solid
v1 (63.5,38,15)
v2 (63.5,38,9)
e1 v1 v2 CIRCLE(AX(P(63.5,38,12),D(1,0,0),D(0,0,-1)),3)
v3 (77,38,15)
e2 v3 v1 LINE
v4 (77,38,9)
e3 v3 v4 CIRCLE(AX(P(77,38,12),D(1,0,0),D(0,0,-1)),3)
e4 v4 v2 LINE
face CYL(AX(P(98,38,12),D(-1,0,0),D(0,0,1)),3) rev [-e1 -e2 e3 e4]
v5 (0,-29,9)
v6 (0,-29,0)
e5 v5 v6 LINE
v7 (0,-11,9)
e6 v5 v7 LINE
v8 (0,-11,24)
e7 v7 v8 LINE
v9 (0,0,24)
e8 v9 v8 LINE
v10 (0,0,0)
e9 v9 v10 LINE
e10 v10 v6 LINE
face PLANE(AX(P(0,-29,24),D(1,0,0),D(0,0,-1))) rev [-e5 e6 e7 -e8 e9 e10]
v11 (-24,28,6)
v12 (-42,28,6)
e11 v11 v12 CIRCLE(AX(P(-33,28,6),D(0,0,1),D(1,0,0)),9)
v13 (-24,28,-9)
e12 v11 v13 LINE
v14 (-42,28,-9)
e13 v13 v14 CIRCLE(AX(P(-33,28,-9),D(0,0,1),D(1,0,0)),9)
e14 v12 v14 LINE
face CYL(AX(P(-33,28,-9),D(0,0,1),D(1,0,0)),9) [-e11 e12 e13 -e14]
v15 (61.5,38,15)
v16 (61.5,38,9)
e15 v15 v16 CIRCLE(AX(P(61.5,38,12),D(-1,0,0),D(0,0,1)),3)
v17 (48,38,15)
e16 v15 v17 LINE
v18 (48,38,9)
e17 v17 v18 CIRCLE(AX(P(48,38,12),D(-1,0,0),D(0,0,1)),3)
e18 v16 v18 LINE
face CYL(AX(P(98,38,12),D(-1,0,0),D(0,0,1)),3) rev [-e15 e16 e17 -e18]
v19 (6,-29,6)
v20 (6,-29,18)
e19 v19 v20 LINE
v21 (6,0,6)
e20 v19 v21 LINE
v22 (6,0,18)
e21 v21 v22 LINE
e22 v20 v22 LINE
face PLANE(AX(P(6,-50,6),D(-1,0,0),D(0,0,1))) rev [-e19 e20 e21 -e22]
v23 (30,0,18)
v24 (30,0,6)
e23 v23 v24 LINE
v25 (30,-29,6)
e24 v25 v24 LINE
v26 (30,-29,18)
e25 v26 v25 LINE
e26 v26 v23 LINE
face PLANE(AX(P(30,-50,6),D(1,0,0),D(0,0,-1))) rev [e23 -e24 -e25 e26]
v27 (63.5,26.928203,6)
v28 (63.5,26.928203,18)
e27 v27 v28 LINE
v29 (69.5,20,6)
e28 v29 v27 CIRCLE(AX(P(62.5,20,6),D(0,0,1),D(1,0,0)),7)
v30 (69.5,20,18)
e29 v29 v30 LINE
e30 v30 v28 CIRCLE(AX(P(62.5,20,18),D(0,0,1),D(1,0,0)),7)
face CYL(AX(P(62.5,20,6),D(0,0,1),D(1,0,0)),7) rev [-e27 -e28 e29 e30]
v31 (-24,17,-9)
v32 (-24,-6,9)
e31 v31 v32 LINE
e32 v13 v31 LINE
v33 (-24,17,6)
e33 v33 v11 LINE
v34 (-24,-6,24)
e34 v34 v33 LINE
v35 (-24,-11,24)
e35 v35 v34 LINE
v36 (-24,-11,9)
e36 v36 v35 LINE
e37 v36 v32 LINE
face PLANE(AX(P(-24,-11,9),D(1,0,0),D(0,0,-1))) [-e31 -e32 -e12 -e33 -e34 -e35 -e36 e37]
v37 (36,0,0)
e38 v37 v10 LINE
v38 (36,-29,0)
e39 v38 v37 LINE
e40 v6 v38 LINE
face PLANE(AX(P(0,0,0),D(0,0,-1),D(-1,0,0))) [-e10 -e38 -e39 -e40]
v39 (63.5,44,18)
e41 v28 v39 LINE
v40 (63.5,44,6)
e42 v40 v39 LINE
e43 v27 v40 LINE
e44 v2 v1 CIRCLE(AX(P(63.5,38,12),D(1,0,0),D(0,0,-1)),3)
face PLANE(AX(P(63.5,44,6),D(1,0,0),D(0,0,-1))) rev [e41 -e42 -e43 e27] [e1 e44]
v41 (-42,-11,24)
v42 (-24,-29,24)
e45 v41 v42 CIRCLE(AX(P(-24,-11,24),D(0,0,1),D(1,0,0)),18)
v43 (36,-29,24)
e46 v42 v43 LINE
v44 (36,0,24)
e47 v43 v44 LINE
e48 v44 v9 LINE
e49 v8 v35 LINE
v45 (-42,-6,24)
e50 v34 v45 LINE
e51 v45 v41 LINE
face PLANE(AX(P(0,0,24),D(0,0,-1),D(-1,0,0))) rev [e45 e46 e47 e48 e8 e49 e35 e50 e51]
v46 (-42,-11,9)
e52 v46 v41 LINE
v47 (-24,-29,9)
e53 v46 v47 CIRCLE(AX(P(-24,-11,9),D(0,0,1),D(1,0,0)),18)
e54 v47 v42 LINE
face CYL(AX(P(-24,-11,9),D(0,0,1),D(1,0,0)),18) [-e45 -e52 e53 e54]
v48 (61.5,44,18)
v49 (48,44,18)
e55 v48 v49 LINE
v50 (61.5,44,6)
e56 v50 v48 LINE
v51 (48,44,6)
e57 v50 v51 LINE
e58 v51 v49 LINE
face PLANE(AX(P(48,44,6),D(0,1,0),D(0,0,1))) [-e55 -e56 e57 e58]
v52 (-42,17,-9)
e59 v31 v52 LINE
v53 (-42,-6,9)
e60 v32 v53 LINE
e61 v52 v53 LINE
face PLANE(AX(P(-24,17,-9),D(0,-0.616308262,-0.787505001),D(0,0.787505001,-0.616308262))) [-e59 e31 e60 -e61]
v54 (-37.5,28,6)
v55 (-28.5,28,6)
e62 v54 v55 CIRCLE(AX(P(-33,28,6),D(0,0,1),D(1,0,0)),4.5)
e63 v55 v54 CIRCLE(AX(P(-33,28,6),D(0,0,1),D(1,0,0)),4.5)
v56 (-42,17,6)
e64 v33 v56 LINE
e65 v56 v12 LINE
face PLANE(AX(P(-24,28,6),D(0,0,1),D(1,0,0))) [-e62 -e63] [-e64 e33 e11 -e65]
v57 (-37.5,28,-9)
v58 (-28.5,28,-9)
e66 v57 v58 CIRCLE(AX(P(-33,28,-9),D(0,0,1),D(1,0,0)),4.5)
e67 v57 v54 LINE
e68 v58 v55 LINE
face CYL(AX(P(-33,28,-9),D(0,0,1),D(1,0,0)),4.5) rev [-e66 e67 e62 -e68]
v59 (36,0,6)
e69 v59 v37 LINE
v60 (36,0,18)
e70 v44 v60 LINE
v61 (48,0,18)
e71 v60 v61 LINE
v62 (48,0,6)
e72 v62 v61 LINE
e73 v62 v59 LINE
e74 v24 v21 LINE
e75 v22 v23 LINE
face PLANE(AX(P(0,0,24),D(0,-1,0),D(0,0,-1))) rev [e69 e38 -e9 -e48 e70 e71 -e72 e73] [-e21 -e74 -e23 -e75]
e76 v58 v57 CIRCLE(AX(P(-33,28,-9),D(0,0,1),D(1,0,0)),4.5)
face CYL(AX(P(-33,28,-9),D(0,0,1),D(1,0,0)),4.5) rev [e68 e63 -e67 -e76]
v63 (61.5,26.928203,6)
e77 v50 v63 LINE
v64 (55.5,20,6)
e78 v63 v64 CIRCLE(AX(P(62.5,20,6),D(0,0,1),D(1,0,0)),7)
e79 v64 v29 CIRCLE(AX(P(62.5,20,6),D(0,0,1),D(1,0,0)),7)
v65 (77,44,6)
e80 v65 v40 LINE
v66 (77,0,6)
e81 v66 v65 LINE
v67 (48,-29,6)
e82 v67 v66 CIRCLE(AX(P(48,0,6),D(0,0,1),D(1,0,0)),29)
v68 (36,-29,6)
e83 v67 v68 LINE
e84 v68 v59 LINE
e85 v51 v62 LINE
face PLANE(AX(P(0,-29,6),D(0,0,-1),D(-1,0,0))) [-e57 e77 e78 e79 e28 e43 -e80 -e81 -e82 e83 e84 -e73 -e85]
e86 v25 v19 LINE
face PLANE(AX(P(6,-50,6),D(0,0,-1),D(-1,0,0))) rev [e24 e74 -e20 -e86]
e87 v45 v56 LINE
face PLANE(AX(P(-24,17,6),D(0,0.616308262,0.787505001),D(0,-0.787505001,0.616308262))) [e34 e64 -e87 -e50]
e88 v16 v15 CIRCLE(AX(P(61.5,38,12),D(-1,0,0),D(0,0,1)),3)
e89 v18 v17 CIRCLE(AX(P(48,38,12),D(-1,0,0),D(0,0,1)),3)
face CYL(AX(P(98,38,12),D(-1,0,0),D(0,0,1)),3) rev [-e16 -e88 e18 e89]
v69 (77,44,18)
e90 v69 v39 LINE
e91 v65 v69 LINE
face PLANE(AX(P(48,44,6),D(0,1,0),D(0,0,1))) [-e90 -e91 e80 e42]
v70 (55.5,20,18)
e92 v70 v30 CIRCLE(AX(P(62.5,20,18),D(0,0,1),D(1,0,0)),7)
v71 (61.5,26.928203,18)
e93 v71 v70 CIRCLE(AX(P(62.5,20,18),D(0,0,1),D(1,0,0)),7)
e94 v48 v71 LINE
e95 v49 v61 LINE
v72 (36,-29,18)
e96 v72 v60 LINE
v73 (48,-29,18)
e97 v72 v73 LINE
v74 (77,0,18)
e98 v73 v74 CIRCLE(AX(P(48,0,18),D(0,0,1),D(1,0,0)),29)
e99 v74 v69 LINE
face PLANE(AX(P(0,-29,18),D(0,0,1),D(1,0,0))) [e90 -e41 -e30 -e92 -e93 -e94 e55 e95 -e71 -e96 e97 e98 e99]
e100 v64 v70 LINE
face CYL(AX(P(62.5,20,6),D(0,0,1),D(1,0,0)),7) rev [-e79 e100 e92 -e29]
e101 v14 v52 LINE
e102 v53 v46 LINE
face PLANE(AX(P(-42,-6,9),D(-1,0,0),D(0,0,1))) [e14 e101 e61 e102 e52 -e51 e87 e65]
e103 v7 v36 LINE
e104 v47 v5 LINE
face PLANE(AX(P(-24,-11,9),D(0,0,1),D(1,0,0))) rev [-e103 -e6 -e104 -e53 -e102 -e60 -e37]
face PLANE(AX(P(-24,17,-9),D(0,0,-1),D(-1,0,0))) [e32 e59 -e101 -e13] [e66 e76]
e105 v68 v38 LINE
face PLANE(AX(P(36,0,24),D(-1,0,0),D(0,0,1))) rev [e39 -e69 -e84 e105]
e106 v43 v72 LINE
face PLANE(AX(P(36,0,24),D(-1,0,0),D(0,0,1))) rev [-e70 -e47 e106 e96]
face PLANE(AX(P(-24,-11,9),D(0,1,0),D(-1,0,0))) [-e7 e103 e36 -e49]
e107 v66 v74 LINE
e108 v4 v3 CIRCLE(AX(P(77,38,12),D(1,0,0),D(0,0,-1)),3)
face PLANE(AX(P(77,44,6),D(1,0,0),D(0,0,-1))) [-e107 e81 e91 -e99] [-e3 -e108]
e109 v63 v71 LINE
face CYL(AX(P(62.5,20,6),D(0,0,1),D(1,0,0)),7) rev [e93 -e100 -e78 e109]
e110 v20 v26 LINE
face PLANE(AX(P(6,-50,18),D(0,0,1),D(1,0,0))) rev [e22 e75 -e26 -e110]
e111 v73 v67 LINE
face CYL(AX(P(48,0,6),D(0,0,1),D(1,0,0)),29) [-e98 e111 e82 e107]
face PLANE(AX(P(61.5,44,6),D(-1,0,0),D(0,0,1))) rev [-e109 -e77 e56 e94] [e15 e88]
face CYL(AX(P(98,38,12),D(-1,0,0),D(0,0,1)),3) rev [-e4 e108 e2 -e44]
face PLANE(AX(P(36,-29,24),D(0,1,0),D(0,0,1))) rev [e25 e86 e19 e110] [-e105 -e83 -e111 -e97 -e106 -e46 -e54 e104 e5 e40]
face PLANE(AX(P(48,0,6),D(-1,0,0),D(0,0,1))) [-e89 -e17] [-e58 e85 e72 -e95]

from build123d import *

# Parameters (mm, degrees)
BASE_BLOCK_SKETCH_W       = 36
BASE_BLOCK_SKETCH_H       = 29
BASE_BLOCK_DEPTH          = 24
OFFSET_ARM_DEPTH          = 15
ARM_RISER_DEPTH           = 18
UPPER_ARM_SKETCH_W        = 15
UPPER_ARM_SKETCH_H        = 11
UPPER_ARM_DEPTH           = 18
PIVOT_LUG_DEPTH           = 15
PIVOT_HOLE_SKETCH_R       = 4.5
PIVOT_HOLE_DEPTH          = 15
CLAMP_BODY_DEPTH          = 29
CLAMP_JAW_SKETCH_W        = 29
CLAMP_JAW_SKETCH_H        = 44
CLAMP_JAW_DEPTH           = 12
CLAMP_JAW_END_DEPTH       = 12
CLAMP_BORE_AND_SLOT_DEPTH = 12
WINDOW_SKETCH_W           = 24
WINDOW_SKETCH_H           = 12
RECTANGULAR_WINDOW_DEPTH  = 50
CROSS_HOLE_SKETCH_R       = 3
CLAMP_CROSS_HOLE_DEPTH    = 50


with BuildPart() as part:
    # Base Block Sketch → Base Block (new body)
    with BuildSketch(Plane.XY):
        with Locations((18, -14.5)):
            Rectangle(BASE_BLOCK_SKETCH_W, BASE_BLOCK_SKETCH_H)
    extrude(amount=BASE_BLOCK_DEPTH)

    # Offset Arm Sketch → Offset Arm (add)
    with BuildSketch(Plane.XY.offset(24)):
        with BuildLine():
            Line((0, -29), (-24, -29))
            ThreePointArc((-24, -29), (-36.727922061, -23.727922061), (-42, -11))
            Line((-42, -11), (-42, -6))
            Line((-42, -6), (-41.291616466, -6))
            Line((-41.291616466, -6), (-24, -6))
            Line((-24, -6), (-24, -11))
            Line((-24, -11), (0, -11))
            Line((0, -11), (0, -29))
        make_face()
    extrude(amount=-OFFSET_ARM_DEPTH)

    # Arm Riser Sketch → Arm Riser (add)
    with BuildSketch(Plane.ZY.offset(42)):
        Polygon((-9, 17), (9, -6), (24, -6), (6, 17), align=None)
    extrude(amount=-ARM_RISER_DEPTH)

    # Upper Arm Sketch → Upper Arm (add)
    with BuildSketch(Plane.ZY.offset(42)):
        with Locations((-1.5, 22.5)):
            Rectangle(UPPER_ARM_SKETCH_W, UPPER_ARM_SKETCH_H)
    extrude(amount=-UPPER_ARM_DEPTH)

    # Pivot Lug Sketch → Pivot Lug (add)
    with BuildSketch(Plane.XY.offset(6)):
        with BuildLine():
            Line((-42, 28), (-24, 28))
            ThreePointArc((-24, 28), (-33, 37), (-42, 28))
        make_face()
    extrude(amount=-PIVOT_LUG_DEPTH)

    # Pivot Hole Sketch → Pivot Hole (cut)
    with BuildSketch(Plane.XY.offset(6)):
        with Locations((-33, 28)):
            Circle(PIVOT_HOLE_SKETCH_R)
    extrude(amount=-PIVOT_HOLE_DEPTH, mode=Mode.SUBTRACT)

    # Clamp Body Sketch → Clamp Body (add)
    with BuildSketch(Plane(origin=(0, 0, 0), x_dir=(1, 0, 0), z_dir=(0, 1, 0))):
        Polygon((36, -6), (36, -12), (36, -18), (48, -18), (48, -6), align=None)
    extrude(amount=-CLAMP_BODY_DEPTH)



with BuildPart() as body_2:
    # Clamp Jaw Sketch → Clamp Jaw (new body)
    with BuildSketch(Plane.XY.offset(18)):
        with Locations((62.5, 22)):
            Rectangle(CLAMP_JAW_SKETCH_W, CLAMP_JAW_SKETCH_H)
    extrude(amount=-CLAMP_JAW_DEPTH)


with BuildPart() as part_1:
    add(part.part)

    add(body_2.part)  # Clamp Jaw End merges body 2
    # Clamp Jaw End Sketch → Clamp Jaw End (add)
    with BuildSketch(Plane.XY.offset(18)):
        with BuildLine():
            Line((48, 0), (77, 0))
            ThreePointArc((77, 0), (68.506096654, -20.506096654), (48, -29))
            Line((48, -29), (48, 0))
        make_face()
    extrude(amount=-CLAMP_JAW_END_DEPTH)

    # Clamp Bore Slot Sketch → Clamp Bore and Slot (cut)
    with BuildSketch(Plane.XY.offset(18)):
        with BuildLine():
            Line((62.5, 44), (61.5, 44))
            Line((61.5, 44), (61.5, 26.92820323))
            ThreePointArc((61.5, 26.92820323), (62.5, 13), (63.5, 26.92820323))
            Line((63.5, 26.92820323), (63.5, 44))
            Line((63.5, 44), (62.5, 44))
        make_face()
    extrude(amount=-CLAMP_BORE_AND_SLOT_DEPTH, mode=Mode.SUBTRACT)

    # Window Sketch → Rectangular Window (cut)
    with BuildSketch(Plane(origin=(0, 0, 0), x_dir=(1, 0, 0), z_dir=(0, 1, 0))):
        with Locations((18, -12)):
            Rectangle(WINDOW_SKETCH_W, WINDOW_SKETCH_H)
    extrude(amount=-RECTANGULAR_WINDOW_DEPTH, mode=Mode.SUBTRACT)

    # Cross Hole Sketch → Clamp Cross Hole (cut)
    with BuildSketch(Plane.ZY.offset(-48)):
        with Locations((12, 38)):
            Circle(CROSS_HOLE_SKETCH_R)
    extrude(amount=-CLAMP_CROSS_HOLE_DEPTH, mode=Mode.SUBTRACT)


solid = part_1.part
